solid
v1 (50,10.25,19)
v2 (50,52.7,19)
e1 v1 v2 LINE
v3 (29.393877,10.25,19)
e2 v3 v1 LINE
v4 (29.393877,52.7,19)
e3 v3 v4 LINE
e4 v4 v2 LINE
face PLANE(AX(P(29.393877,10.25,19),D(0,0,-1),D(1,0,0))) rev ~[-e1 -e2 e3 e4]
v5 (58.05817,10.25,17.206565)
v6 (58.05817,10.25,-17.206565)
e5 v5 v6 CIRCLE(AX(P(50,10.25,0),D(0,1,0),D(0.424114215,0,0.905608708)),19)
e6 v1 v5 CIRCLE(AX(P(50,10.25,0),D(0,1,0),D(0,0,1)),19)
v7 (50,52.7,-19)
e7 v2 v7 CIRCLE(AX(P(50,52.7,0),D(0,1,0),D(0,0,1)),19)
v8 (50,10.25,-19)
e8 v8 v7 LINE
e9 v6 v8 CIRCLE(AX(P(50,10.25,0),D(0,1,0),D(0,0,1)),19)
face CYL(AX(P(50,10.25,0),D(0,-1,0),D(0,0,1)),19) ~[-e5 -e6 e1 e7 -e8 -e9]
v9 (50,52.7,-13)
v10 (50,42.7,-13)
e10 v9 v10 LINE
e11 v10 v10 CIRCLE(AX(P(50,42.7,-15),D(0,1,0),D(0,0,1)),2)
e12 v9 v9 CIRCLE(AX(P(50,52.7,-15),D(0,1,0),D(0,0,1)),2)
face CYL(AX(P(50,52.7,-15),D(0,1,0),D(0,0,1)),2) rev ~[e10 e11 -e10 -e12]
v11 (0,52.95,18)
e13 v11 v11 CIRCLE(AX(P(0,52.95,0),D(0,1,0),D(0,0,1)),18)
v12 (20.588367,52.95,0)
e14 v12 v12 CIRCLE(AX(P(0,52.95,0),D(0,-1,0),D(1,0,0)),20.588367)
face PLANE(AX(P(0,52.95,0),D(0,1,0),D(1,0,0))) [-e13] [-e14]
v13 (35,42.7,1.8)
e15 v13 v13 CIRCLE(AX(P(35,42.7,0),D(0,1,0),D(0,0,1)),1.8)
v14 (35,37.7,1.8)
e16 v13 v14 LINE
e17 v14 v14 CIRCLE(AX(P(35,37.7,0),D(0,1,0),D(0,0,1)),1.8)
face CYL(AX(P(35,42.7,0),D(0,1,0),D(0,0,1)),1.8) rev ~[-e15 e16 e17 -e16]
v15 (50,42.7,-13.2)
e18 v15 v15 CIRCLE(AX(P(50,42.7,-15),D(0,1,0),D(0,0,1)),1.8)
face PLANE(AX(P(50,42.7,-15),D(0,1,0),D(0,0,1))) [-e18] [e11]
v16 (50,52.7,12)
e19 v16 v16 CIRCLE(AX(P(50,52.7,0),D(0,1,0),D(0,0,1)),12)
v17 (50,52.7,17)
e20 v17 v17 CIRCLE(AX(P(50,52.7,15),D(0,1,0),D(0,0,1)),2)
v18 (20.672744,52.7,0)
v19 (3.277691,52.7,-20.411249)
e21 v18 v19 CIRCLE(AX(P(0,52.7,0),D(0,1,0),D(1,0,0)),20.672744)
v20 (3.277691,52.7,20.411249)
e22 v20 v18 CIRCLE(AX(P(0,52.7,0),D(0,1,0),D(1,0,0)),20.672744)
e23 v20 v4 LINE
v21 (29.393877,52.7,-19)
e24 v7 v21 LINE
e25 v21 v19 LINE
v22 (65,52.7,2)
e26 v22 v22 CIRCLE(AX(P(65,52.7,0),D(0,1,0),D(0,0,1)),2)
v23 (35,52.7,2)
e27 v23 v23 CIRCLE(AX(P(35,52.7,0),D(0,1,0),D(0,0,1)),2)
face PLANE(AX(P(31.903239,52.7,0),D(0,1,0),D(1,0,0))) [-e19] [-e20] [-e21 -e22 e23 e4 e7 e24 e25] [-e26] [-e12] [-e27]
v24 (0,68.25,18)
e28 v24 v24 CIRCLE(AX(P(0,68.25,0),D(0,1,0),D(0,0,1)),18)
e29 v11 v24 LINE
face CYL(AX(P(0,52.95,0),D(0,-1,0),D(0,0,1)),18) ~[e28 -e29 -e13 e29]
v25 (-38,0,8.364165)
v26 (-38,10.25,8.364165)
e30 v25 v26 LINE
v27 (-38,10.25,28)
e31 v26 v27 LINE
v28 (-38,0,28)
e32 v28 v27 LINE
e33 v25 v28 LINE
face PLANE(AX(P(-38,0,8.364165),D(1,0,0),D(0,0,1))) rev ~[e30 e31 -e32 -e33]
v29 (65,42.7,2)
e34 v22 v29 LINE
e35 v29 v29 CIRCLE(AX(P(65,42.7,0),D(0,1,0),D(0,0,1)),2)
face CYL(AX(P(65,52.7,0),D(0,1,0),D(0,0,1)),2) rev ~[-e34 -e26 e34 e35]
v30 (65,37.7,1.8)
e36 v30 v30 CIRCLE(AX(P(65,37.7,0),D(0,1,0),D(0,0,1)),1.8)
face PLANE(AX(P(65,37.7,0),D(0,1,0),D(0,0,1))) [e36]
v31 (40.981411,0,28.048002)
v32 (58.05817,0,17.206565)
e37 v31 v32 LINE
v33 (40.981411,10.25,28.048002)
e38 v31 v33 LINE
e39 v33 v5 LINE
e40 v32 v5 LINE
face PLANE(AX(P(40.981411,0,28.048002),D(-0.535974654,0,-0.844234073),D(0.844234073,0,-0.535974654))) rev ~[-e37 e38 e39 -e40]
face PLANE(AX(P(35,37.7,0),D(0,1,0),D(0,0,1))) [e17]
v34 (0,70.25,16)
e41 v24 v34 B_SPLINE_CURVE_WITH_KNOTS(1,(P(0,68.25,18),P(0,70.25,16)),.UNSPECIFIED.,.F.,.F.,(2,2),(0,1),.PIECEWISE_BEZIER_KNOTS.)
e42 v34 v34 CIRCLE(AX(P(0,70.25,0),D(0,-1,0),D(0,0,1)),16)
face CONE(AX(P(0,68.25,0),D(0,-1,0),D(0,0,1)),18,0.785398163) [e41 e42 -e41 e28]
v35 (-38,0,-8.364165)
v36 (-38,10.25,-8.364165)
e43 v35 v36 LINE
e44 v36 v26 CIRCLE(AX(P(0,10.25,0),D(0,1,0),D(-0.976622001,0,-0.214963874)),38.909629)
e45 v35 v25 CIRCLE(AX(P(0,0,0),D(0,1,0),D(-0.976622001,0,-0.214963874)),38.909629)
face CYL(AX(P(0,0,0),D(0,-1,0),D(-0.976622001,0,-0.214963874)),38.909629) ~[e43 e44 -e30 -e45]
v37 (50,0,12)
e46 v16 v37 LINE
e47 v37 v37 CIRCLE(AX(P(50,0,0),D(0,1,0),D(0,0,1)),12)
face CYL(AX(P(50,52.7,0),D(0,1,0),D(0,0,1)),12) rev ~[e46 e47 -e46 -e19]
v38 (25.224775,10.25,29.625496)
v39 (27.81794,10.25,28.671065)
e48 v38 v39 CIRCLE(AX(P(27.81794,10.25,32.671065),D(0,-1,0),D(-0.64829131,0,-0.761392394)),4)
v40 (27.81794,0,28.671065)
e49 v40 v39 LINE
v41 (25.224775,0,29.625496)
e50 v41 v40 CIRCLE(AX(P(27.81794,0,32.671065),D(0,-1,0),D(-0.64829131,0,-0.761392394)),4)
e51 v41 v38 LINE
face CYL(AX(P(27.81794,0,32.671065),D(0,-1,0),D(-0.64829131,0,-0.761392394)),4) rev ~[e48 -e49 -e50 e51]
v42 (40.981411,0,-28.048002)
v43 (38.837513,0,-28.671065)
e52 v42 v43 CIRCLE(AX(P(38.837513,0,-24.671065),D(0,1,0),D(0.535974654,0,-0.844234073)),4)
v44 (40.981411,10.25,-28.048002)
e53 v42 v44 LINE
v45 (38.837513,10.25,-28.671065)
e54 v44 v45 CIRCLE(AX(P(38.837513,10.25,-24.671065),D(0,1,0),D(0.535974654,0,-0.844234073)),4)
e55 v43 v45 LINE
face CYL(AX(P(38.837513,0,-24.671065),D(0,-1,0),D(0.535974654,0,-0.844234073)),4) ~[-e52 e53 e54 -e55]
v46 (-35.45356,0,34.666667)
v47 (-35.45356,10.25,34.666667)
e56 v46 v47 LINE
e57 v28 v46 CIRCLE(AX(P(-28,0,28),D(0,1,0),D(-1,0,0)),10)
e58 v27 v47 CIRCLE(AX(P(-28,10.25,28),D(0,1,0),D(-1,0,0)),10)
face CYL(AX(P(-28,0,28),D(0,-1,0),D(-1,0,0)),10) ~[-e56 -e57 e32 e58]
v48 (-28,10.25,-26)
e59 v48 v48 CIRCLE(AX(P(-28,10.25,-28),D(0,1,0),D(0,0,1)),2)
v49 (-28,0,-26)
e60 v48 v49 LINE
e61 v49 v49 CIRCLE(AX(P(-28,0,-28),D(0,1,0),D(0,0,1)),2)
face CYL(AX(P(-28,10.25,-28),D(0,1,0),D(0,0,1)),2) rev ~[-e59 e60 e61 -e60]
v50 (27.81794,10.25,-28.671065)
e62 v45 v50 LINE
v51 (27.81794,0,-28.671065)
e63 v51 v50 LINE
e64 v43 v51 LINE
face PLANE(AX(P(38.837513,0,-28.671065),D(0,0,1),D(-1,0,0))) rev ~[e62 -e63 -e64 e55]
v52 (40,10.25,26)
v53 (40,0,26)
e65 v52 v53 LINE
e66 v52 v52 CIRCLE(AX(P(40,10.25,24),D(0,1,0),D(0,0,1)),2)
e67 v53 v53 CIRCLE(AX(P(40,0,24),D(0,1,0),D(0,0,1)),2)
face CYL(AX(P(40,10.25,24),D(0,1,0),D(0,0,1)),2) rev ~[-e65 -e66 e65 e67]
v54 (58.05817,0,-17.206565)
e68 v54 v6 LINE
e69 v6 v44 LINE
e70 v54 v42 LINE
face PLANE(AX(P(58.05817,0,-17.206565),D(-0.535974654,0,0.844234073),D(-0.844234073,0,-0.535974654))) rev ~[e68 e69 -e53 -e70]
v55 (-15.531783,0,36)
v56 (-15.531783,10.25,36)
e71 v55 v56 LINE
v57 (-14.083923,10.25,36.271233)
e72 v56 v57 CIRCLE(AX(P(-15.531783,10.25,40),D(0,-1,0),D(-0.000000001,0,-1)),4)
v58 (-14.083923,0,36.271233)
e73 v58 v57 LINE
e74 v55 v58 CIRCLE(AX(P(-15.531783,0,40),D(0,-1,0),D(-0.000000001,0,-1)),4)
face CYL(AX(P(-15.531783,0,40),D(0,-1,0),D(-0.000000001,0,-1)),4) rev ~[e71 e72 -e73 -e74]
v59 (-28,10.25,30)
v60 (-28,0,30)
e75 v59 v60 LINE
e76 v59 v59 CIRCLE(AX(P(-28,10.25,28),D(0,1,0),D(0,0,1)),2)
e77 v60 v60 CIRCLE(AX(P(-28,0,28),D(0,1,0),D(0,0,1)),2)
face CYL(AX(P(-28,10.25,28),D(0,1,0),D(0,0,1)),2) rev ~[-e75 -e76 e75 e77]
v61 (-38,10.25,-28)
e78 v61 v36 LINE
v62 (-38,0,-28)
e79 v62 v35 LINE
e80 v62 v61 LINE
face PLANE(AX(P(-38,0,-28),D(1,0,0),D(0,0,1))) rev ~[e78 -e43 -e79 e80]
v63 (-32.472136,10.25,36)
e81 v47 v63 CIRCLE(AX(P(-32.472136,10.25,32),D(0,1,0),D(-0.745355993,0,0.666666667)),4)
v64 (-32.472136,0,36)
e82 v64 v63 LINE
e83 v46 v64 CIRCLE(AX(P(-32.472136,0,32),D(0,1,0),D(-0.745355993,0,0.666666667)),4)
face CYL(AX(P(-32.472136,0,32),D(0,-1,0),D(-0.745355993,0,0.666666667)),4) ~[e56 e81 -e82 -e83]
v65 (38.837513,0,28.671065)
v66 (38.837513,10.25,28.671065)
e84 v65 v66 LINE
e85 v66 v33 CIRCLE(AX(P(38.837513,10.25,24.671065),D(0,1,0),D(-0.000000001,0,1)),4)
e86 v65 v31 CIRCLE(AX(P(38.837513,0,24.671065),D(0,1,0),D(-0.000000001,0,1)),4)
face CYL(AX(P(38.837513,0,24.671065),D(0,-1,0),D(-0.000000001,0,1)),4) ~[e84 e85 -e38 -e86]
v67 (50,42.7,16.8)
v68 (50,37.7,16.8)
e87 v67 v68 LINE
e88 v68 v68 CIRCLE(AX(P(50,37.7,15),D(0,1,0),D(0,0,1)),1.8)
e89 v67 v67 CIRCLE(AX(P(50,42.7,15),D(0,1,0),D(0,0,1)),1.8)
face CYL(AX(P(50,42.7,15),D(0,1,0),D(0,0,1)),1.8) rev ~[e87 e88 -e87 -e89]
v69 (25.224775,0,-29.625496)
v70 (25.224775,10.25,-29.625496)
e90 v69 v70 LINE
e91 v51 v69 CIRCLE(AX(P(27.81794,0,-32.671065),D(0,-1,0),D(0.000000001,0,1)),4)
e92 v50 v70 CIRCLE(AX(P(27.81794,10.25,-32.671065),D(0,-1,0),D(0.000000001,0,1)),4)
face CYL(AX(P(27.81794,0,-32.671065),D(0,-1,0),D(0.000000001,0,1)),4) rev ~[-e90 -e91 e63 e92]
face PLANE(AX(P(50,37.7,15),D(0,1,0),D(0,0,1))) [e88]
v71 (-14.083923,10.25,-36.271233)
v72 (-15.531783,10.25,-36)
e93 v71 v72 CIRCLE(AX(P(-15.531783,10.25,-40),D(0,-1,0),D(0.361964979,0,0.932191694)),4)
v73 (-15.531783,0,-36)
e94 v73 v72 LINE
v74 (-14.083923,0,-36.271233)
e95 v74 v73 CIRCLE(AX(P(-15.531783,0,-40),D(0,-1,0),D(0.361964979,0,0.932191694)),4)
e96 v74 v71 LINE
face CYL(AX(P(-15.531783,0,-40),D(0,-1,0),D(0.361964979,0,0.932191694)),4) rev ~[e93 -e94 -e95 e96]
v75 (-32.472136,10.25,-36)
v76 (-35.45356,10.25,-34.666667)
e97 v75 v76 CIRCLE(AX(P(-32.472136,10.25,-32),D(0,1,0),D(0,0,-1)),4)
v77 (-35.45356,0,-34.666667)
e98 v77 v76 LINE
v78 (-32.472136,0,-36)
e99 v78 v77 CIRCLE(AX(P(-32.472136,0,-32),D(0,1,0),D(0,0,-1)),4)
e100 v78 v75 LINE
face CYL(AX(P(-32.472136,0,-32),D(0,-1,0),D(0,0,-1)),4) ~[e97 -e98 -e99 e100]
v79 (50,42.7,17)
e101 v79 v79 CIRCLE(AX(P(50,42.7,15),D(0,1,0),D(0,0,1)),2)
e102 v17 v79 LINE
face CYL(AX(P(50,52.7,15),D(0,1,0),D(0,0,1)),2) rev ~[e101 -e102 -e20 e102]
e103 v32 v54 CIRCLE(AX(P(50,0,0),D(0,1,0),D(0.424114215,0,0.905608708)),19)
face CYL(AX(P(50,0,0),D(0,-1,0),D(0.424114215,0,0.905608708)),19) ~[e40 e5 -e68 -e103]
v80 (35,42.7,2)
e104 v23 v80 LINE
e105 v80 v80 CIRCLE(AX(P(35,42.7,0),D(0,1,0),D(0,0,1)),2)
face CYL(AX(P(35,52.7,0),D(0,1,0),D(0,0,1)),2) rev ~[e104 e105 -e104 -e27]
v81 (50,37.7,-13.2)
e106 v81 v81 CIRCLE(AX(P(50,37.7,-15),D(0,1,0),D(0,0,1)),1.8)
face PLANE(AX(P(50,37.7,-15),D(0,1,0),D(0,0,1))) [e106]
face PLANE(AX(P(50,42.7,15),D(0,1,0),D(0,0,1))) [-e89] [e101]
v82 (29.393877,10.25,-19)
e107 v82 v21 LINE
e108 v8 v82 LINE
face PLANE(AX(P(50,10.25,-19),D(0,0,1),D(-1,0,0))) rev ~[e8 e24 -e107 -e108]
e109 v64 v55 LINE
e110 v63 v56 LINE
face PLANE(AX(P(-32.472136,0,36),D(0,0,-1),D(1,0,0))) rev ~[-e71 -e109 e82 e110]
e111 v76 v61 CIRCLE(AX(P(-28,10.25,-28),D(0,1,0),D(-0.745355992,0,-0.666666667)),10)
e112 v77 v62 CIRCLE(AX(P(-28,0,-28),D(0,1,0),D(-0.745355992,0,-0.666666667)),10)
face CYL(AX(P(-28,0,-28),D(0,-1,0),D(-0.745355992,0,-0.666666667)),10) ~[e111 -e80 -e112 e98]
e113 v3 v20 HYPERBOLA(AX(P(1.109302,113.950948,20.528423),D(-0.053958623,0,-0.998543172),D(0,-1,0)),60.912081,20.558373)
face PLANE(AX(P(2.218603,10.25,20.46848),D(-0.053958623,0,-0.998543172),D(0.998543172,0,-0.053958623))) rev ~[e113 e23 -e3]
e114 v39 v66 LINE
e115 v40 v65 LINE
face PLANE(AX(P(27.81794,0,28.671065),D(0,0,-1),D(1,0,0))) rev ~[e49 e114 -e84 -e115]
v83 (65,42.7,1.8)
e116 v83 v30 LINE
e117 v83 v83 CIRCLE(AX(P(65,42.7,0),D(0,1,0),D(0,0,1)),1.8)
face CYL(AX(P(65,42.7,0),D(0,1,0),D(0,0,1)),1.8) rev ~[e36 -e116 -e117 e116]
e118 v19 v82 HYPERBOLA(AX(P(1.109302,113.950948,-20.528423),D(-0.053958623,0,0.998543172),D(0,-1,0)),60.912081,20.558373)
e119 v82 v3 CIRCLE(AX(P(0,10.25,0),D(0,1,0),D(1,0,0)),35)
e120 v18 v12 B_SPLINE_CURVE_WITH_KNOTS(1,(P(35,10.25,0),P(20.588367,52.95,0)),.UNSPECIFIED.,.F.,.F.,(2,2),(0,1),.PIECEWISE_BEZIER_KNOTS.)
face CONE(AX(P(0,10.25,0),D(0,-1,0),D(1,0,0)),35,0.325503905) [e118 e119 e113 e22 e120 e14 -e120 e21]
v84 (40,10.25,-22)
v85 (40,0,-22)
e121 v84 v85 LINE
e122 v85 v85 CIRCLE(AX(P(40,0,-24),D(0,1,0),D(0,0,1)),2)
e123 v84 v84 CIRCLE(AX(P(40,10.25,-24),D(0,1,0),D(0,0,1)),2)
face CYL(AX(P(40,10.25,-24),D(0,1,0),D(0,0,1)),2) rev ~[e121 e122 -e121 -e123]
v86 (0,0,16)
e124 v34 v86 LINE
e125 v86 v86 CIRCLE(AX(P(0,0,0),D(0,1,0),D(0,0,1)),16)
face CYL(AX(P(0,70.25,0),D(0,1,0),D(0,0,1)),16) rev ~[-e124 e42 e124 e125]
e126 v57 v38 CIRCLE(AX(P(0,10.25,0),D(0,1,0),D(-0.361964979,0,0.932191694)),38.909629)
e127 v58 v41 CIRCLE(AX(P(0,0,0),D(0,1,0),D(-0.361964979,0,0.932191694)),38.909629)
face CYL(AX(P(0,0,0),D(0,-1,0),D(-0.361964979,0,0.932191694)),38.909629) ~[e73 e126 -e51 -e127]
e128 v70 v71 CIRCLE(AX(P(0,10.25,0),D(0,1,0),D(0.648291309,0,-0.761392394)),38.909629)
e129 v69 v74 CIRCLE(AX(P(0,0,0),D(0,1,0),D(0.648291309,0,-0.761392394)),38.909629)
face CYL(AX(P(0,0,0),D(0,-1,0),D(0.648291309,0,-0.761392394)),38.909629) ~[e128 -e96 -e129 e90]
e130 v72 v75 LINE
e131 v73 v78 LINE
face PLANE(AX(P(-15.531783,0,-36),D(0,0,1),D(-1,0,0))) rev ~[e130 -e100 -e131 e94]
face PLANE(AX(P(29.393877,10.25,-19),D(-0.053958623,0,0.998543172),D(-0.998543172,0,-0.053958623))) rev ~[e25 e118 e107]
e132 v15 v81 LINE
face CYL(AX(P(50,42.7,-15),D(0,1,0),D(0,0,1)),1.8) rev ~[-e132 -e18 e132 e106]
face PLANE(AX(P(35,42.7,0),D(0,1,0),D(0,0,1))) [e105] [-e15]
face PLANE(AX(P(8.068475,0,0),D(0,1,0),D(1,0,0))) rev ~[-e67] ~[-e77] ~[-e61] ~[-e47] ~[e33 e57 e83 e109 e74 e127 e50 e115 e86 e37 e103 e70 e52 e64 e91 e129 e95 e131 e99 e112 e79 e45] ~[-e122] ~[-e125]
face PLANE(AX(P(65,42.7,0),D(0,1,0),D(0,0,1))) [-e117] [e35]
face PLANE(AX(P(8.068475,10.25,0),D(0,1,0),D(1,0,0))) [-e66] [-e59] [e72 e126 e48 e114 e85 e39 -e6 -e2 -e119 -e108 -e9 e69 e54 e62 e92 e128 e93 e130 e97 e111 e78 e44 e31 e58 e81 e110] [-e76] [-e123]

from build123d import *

# Parameters (mm, degrees)
BASE_FLANGE_DEPTH                 = 10.25
TAPERED_COLUMN_SKETCH_R           = 35
TAPERED_COLUMN_DEPTH              = 42.7
TAPERED_COLUMN_TAPER              = 18.65
TOP_BOSS_SKETCH_R                 = 18
TOP_BOSS_DEPTH                    = 15.3
TOP_COLLAR_SKETCH_R               = 18
TOP_COLLAR_45DEG_TAPER_DEPTH      = 2
TOP_COLLAR_45DEG_TAPER_TAPER      = 45
SIDE_BOSS_DEPTH                   = 42.45
SIDE_BOSS_HOLES_SKETCH_R          = 2
SIDE_BOSS_HOLES_4X_DEPTH_10_DEPTH = 10
SECONDARY_HOLES_SKETCH_R          = 1.8
SECONDARY_HOLES_4X_DEPTH_5_DEPTH  = 5
SIDE_BORE_SKETCH_R                = 12
SIDE_BORE_DEPTH                   = 177
MAIN_BORE_SKETCH_R                = 16
MAIN_BORE_DEPTH                   = 177
FLANGE_HOLES_SKETCH_R             = 2
FLANGE_HOLES_4X_DEPTH             = 177


with BuildPart() as part:
    # Base Flange Sketch → Base Flange (new body)
    with BuildSketch(Plane(origin=(0, 0, 0), x_dir=(1, 0, 0), z_dir=(0, 1, 0))):
        with BuildLine():
            Line((58.058170092, 17.206565455), (40.981411355, 28.048001668))
            ThreePointArc((40.981411355, 28.048001668), (39.953813512, 28.512142384), (38.837512739, 28.671065375))
            Line((38.837512739, 28.671065375), (27.817939746, 28.671065375))
            ThreePointArc((27.817939746, 28.671065375), (26.436324443, 28.917248763), (25.224774509, 29.625495798))
            ThreePointArc((25.224774509, 29.625495798), (6.486223775, 38.365194531), (-14.083923128, 36.271233224))
            ThreePointArc((-14.083923128, 36.271233224), (-14.795259826, 36.068393006), (-15.531783042, 36))
            Line((-15.531783042, 36), (-28, 36))
            Line((-28, 36), (-32.472135955, 36))
            ThreePointArc((-32.472135955, 36), (-34.105129117, 35.651483717), (-35.453559925, 34.666666667))
            ThreePointArc((-35.453559925, 34.666666667), (-37.34172359, 31.568220898), (-38, 28))
            Line((-38, 28), (-38, 8.364164649))
            ThreePointArc((-38, 8.364164649), (-38.909629274, 0), (-38, -8.364164649))
            Line((-38, -8.364164649), (-38, -28))
            ThreePointArc((-38, -28), (-37.34172359, -31.568220898), (-35.453559925, -34.666666667))
            ThreePointArc((-35.453559925, -34.666666667), (-34.105129117, -35.651483717), (-32.472135955, -36))
            Line((-32.472135955, -36), (-28, -36))
            Line((-28, -36), (-15.531783042, -36))
            ThreePointArc((-15.531783042, -36), (-14.795259826, -36.068393006), (-14.083923128, -36.271233224))
            ThreePointArc((-14.083923128, -36.271233224), (6.486223775, -38.365194531), (25.224774509, -29.625495798))
            ThreePointArc((25.224774509, -29.625495798), (26.436324443, -28.917248763), (27.817939746, -28.671065375))
            Line((27.817939746, -28.671065375), (38.837512739, -28.671065375))
            ThreePointArc((38.837512739, -28.671065375), (39.953813512, -28.512142384), (40.981411355, -28.048001668))
            Line((40.981411355, -28.048001668), (58.058170092, -17.206565455))
            ThreePointArc((58.058170092, -17.206565455), (69, 0), (58.058170092, 17.206565455))
        make_face()
    extrude(amount=BASE_FLANGE_DEPTH)

    # Tapered Column Sketch → Tapered Column (add)
    with BuildSketch(Plane(origin=(0, 10.25, 0), x_dir=(1, 0, 0), z_dir=(0, 1, 0))):
        Circle(TAPERED_COLUMN_SKETCH_R)
    extrude(amount=TAPERED_COLUMN_DEPTH, taper=TAPERED_COLUMN_TAPER)

    # Top Boss Sketch → Top Boss (add)
    with BuildSketch(Plane(origin=(0, 52.95, 0), x_dir=(1, 0, 0), z_dir=(0, 1, 0))):
        with Locations(Location((0, 0, 0), (0, 0, 270))):
            Circle(TOP_BOSS_SKETCH_R)
    extrude(amount=TOP_BOSS_DEPTH)

    # Top Collar Sketch → Top Collar 45deg Taper (add)
    with BuildSketch(Plane(origin=(0, 68.25, 0), x_dir=(1, 0, 0), z_dir=(0, 1, 0))):
        with Locations(Location((0, 0, 0), (0, 0, 270))):
            Circle(TOP_COLLAR_SKETCH_R)
    extrude(amount=TOP_COLLAR_45DEG_TAPER_DEPTH, taper=TOP_COLLAR_45DEG_TAPER_TAPER)

    # Side Boss Sketch → Side Boss (add)
    with BuildSketch(Plane(origin=(0, 10.25, 0), x_dir=(1, 0, 0), z_dir=(0, 1, 0))):
        with BuildLine():
            ThreePointArc((50, -19), (69, 0), (50, 19))
            Line((50, 19), (29.393876913, 19))
            Line((29.393876913, 19), (2.218603036, 20.468479678))
            ThreePointArc((2.218603036, 20.468479678), (20.588367098, 0), (2.218603036, -20.468479678))
            Line((2.218603036, -20.468479678), (29.393876913, -19))
            Line((29.393876913, -19), (50, -19))
        make_face()
    extrude(amount=SIDE_BOSS_DEPTH)

    # Side Boss Holes Sketch → Side Boss Holes 4x Depth 10 (cut)
    with BuildSketch(Plane(origin=(0, 52.7, 0), x_dir=(1, 0, 0), z_dir=(0, 1, 0))):
        with Locations(Location((35, 0, 0), (0, 0, 270))):
            Circle(SIDE_BOSS_HOLES_SKETCH_R)
        with Locations(Location((50, 15, 0), (0, 0, 270))):
            Circle(SIDE_BOSS_HOLES_SKETCH_R)
        with Locations(Location((65, 0, 0), (0, 0, 270))):
            Circle(SIDE_BOSS_HOLES_SKETCH_R)
        with Locations(Location((50, -15, 0), (0, 0, 270))):
            Circle(SIDE_BOSS_HOLES_SKETCH_R)
    extrude(amount=-SIDE_BOSS_HOLES_4X_DEPTH_10_DEPTH, mode=Mode.SUBTRACT)

    # Secondary Holes Sketch → Secondary Holes 4x Depth 5 (cut)
    with BuildSketch(Plane(origin=(0, 42.7, 0), x_dir=(1, 0, 0), z_dir=(0, 1, 0))):
        with Locations(Location((35, 0, 0), (0, 0, 270))):
            Circle(SECONDARY_HOLES_SKETCH_R)
        with Locations(Location((65, 0, 0), (0, 0, 270))):
            Circle(SECONDARY_HOLES_SKETCH_R)
        with Locations(Location((50, -15, 0), (0, 0, 270))):
            Circle(SECONDARY_HOLES_SKETCH_R)
        with Locations(Location((50, 15, 0), (0, 0, 270))):
            Circle(SECONDARY_HOLES_SKETCH_R)
    extrude(amount=-SECONDARY_HOLES_4X_DEPTH_5_DEPTH, mode=Mode.SUBTRACT)

    # Side Bore Sketch → Side Bore (cut)
    with BuildSketch(Plane(origin=(0, 52.7, 0), x_dir=(1, 0, 0), z_dir=(0, 1, 0))):
        with Locations(Location((50, 0, 0), (0, 0, 270))):
            Circle(SIDE_BORE_SKETCH_R)
    extrude(amount=-SIDE_BORE_DEPTH, mode=Mode.SUBTRACT)

    # Main Bore Sketch → Main Bore (cut)
    with BuildSketch(Plane(origin=(0, 70.25, 0), x_dir=(1, 0, 0), z_dir=(0, 1, 0))):
        with Locations(Location((0, 0, 0), (0, 0, 270))):
            Circle(MAIN_BORE_SKETCH_R)
    extrude(amount=-MAIN_BORE_DEPTH, mode=Mode.SUBTRACT)

    # Flange Holes Sketch → Flange Holes 4x (cut)
    with BuildSketch(Plane(origin=(0, 10.25, 0), x_dir=(1, 0, 0), z_dir=(0, 1, 0))):
        with Locations(Location((40, -24, 0), (0, 0, 270))):
            Circle(FLANGE_HOLES_SKETCH_R)
        with Locations(Location((40, 24, 0), (0, 0, 270))):
            Circle(FLANGE_HOLES_SKETCH_R)
        with Locations(Location((-28, 28, 0), (0, 0, 270))):
            Circle(FLANGE_HOLES_SKETCH_R)
        with Locations(Location((-28, -28, 0), (0, 0, 270))):
            Circle(FLANGE_HOLES_SKETCH_R)
    extrude(amount=-FLANGE_HOLES_4X_DEPTH, mode=Mode.SUBTRACT)


solid = part.part
